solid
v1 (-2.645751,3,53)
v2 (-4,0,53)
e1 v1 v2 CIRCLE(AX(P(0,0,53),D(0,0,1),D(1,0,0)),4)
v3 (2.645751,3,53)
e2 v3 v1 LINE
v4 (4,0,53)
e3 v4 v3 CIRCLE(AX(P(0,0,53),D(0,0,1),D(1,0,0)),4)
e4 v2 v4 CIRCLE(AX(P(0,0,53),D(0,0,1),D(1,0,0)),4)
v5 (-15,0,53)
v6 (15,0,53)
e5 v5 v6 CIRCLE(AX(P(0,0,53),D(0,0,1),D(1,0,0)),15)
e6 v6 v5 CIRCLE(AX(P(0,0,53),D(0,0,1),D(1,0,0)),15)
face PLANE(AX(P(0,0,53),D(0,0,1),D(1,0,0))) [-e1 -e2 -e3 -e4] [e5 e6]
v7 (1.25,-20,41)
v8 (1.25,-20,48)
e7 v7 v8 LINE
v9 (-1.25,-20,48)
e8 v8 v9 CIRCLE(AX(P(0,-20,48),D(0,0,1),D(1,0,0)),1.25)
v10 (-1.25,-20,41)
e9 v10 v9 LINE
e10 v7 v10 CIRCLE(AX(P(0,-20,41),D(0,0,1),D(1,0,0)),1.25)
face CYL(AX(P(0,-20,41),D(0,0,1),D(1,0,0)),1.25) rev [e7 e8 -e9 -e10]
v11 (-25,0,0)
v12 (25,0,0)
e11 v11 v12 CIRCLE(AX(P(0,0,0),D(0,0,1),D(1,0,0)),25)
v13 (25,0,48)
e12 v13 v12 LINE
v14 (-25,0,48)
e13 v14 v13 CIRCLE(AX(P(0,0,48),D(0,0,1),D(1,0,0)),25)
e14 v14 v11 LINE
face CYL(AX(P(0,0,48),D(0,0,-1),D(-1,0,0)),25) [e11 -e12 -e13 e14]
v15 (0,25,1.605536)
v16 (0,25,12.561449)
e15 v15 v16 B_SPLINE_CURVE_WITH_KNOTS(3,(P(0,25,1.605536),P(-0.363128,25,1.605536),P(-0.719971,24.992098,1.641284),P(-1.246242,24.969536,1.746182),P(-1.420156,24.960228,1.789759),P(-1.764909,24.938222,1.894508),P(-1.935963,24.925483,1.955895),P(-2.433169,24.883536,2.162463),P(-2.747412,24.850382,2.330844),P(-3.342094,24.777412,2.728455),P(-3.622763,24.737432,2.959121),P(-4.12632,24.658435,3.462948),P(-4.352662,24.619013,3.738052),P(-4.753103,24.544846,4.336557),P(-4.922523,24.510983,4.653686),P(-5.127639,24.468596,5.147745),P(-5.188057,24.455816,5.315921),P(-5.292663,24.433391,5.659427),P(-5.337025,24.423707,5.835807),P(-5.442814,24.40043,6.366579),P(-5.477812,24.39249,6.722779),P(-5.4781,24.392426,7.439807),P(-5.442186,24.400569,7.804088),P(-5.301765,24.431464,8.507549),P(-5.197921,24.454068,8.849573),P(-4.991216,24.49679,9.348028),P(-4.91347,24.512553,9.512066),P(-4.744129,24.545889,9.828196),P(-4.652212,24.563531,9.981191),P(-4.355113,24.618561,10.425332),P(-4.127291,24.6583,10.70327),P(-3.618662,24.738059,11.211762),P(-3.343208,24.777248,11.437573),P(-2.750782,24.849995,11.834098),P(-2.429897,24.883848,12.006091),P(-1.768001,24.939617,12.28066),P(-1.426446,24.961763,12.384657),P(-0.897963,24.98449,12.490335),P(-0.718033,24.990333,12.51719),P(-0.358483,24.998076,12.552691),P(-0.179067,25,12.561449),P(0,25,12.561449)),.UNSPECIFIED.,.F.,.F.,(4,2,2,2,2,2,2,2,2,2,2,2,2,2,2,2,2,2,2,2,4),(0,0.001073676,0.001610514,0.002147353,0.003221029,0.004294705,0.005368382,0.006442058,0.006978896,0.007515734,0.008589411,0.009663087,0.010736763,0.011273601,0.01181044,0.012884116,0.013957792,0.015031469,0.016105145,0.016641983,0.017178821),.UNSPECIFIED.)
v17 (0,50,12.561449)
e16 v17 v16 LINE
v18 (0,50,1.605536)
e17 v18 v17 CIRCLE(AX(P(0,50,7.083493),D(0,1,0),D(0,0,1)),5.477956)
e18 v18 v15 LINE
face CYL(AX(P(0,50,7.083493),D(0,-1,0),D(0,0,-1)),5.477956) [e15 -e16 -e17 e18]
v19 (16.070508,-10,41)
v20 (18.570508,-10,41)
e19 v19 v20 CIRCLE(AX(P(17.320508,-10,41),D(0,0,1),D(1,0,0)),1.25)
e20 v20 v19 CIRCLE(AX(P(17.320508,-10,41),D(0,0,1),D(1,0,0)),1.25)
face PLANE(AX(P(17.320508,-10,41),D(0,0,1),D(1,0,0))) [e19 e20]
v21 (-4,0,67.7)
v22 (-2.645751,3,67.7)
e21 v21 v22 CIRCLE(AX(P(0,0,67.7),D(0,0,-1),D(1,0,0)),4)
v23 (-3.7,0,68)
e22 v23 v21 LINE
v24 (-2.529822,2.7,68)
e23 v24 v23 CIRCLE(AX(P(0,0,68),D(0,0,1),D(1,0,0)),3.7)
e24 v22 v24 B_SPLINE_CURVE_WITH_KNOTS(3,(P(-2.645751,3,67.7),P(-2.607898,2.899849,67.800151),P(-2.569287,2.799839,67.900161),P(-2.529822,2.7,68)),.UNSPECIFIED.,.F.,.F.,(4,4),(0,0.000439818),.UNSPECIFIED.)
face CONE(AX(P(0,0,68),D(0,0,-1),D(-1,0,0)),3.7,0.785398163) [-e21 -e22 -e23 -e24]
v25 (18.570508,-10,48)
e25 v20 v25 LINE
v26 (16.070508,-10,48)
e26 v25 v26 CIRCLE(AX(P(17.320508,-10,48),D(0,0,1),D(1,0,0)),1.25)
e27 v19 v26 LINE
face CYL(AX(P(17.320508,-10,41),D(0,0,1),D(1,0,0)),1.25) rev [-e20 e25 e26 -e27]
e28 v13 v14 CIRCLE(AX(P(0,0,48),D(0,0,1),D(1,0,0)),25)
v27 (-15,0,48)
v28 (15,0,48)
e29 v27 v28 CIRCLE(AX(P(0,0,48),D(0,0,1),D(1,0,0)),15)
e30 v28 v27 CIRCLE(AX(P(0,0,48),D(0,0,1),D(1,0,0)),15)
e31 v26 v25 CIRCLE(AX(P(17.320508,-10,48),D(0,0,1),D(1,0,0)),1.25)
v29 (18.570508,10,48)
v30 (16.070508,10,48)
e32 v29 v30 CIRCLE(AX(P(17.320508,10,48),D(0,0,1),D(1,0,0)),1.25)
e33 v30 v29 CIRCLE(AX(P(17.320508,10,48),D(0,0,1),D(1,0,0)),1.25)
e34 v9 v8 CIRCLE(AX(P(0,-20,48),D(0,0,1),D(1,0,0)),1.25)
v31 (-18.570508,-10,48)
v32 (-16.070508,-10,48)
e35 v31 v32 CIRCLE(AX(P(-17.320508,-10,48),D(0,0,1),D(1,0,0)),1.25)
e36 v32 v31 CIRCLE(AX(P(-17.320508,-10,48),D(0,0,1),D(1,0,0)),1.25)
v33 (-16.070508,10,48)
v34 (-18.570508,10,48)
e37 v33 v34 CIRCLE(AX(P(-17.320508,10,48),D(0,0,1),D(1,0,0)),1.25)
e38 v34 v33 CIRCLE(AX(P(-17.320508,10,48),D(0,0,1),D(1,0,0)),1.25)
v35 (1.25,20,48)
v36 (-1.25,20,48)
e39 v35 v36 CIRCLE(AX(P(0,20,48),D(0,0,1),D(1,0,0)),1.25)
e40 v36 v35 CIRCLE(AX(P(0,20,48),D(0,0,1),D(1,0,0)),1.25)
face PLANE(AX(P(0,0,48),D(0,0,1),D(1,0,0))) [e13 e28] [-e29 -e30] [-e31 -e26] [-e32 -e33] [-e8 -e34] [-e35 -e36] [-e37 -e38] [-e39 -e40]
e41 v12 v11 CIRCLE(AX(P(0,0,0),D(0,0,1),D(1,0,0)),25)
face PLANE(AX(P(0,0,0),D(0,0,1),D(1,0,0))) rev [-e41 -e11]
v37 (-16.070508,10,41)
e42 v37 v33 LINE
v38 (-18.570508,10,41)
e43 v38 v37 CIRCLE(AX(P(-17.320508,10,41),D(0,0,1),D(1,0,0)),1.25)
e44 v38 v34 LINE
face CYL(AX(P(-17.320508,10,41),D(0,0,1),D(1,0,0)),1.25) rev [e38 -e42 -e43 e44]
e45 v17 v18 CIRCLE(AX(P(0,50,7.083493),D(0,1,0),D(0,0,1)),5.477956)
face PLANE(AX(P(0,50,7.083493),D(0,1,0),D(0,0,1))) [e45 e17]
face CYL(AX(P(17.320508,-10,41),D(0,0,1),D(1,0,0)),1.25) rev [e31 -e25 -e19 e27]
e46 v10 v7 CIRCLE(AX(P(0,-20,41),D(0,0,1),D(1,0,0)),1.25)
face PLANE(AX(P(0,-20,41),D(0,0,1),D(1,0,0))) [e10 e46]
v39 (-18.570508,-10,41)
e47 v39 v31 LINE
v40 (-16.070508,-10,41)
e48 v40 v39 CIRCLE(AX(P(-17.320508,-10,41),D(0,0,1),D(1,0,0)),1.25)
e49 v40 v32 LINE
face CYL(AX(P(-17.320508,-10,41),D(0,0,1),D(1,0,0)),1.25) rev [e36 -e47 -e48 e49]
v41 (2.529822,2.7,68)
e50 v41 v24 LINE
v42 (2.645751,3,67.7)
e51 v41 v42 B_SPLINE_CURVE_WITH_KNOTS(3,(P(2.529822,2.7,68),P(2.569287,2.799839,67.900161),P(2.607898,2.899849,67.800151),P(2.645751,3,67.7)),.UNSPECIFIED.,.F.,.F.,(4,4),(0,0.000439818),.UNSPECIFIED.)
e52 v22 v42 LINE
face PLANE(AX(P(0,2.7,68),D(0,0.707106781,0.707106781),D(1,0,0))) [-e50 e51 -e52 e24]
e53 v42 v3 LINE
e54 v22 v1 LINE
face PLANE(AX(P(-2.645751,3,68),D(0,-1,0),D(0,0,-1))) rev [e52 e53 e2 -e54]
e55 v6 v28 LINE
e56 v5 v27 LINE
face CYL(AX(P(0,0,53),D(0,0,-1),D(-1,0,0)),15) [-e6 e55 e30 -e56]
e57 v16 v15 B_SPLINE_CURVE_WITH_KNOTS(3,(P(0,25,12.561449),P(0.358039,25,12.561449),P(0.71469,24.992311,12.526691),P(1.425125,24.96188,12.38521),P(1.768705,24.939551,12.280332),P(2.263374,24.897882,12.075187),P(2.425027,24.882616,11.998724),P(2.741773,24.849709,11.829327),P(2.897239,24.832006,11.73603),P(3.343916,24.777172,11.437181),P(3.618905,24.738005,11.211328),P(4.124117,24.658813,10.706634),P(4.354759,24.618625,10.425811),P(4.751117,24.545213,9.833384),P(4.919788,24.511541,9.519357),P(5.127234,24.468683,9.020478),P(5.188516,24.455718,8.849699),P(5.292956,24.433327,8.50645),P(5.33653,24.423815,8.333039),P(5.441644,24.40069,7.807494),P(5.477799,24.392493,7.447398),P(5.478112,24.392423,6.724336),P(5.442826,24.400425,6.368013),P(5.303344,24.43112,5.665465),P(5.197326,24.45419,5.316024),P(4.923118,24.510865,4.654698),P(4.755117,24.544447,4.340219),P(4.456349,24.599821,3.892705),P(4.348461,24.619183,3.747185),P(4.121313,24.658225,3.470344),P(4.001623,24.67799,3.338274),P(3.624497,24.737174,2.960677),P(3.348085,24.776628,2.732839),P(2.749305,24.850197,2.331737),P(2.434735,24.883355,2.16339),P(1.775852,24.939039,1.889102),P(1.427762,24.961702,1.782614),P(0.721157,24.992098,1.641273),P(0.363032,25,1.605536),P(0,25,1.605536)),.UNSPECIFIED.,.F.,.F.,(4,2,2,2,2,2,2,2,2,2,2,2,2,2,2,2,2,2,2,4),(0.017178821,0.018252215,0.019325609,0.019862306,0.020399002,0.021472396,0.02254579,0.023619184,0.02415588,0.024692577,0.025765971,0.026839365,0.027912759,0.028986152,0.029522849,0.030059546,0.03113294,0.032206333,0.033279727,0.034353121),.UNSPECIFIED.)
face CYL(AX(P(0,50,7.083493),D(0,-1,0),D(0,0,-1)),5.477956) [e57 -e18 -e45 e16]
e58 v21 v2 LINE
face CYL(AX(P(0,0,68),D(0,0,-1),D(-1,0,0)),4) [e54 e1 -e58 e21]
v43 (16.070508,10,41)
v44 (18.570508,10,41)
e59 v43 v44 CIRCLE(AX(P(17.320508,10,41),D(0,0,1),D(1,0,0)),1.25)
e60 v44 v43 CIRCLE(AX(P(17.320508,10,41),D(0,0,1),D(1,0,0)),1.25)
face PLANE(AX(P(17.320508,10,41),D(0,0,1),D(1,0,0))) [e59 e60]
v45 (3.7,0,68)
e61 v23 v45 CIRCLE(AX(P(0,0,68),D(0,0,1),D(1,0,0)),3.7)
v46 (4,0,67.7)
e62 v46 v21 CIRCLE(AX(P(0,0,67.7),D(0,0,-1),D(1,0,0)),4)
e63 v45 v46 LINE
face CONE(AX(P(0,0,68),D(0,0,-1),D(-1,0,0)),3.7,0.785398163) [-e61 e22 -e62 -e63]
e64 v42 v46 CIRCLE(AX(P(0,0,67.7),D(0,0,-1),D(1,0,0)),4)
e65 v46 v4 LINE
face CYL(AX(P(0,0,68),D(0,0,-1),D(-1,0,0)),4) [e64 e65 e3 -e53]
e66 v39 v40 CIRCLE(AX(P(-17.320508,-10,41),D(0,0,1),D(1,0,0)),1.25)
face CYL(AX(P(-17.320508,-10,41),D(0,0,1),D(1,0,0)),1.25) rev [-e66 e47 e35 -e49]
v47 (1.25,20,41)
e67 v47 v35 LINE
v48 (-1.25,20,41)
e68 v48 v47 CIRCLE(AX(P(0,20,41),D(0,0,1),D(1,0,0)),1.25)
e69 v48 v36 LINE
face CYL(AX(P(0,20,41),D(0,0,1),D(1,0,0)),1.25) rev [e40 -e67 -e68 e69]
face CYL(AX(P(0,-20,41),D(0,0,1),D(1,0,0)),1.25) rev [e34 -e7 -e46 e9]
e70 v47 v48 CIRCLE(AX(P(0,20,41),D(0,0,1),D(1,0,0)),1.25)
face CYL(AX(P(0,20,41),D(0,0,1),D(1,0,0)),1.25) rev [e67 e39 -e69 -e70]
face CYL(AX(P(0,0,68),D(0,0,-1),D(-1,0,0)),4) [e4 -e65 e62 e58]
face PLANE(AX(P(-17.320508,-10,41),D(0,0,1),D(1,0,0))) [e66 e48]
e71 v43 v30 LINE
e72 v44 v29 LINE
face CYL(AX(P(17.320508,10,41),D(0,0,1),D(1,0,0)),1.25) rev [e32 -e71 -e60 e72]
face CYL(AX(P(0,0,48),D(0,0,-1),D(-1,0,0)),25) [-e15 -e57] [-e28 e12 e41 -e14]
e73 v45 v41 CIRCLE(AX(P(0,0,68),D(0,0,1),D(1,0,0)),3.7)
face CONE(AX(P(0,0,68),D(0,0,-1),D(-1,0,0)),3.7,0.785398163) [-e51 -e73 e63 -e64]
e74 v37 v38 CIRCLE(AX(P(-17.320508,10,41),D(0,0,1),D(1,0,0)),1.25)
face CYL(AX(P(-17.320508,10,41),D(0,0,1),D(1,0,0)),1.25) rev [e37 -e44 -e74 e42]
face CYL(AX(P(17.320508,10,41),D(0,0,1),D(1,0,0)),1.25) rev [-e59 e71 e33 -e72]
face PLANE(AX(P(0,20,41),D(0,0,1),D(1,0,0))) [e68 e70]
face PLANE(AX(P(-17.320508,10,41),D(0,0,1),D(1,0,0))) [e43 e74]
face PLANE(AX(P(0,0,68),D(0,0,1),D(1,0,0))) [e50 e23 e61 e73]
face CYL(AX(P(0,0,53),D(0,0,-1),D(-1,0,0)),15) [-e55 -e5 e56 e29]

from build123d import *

# Parameters (mm, degrees)
SKETCH1_R           = 25
BOSS_EXTRUDE1_DEPTH = 48
SKETCH2_R           = 15
BOSS_EXTRUDE2_DEPTH = 5
BOSS_EXTRUDE3_DEPTH = 15
CHAMFER1_SIZE       = 0.3
SKETCH4_R           = 5.477956266
BOSS_EXTRUDE4_DEPTH = 50
SKETCH5_R           = 1.25
CUT_EXTRUDE1_DEPTH  = 7


with BuildPart() as part:
    # Sketch1 → Boss-Extrude1 (new body)
    with BuildSketch(Plane.XY):
        Circle(SKETCH1_R)
    extrude(amount=BOSS_EXTRUDE1_DEPTH)

    # Sketch2 → Boss-Extrude2 (add)
    with BuildSketch(Plane.XY.offset(48)):
        Circle(SKETCH2_R)
    extrude(amount=BOSS_EXTRUDE2_DEPTH)

    # Sketch3 → Boss-Extrude3 (add)
    with BuildSketch(Plane.XY.offset(53)):
        with BuildLine():
            Line((-2.645751311, 3), (2.645751311, 3))
            ThreePointArc((2.645751311, 3), (0, -4), (-2.645751311, 3))
        make_face()
    extrude(amount=BOSS_EXTRUDE3_DEPTH)

    # Chamfer1
    chamfer1_edges = [part.edges().sort_by_distance(p)[0] for p in [
        (0, -4, 68),
        (0, 3, 68),
    ]]
    chamfer(chamfer1_edges, length=CHAMFER1_SIZE)

    # Sketch4 → Boss-Extrude4 (add)
    with BuildSketch(Plane(origin=(0, 0, 0), x_dir=(1, 0, 0), z_dir=(0, 1, 0))):
        with Locations(Location((0, -7.083492504, 0), (0, 0, 90))):
            Circle(SKETCH4_R)
    extrude(amount=BOSS_EXTRUDE4_DEPTH)

    # Sketch5 → Cut-Extrude1 (cut)
    with BuildSketch(Plane.XY.offset(48)):
        with Locations((0, 20)):
            Circle(SKETCH5_R)
        with Locations((17.320508076, 10)):
            Circle(SKETCH5_R)
        with Locations((17.320508076, -10)):
            Circle(SKETCH5_R)
        with Locations((0, -20)):
            Circle(SKETCH5_R)
        with Locations((-17.320508076, -10)):
            Circle(SKETCH5_R)
        with Locations((-17.320508076, 10)):
            Circle(SKETCH5_R)
    extrude(amount=-CUT_EXTRUDE1_DEPTH, mode=Mode.SUBTRACT)


solid = part.part
